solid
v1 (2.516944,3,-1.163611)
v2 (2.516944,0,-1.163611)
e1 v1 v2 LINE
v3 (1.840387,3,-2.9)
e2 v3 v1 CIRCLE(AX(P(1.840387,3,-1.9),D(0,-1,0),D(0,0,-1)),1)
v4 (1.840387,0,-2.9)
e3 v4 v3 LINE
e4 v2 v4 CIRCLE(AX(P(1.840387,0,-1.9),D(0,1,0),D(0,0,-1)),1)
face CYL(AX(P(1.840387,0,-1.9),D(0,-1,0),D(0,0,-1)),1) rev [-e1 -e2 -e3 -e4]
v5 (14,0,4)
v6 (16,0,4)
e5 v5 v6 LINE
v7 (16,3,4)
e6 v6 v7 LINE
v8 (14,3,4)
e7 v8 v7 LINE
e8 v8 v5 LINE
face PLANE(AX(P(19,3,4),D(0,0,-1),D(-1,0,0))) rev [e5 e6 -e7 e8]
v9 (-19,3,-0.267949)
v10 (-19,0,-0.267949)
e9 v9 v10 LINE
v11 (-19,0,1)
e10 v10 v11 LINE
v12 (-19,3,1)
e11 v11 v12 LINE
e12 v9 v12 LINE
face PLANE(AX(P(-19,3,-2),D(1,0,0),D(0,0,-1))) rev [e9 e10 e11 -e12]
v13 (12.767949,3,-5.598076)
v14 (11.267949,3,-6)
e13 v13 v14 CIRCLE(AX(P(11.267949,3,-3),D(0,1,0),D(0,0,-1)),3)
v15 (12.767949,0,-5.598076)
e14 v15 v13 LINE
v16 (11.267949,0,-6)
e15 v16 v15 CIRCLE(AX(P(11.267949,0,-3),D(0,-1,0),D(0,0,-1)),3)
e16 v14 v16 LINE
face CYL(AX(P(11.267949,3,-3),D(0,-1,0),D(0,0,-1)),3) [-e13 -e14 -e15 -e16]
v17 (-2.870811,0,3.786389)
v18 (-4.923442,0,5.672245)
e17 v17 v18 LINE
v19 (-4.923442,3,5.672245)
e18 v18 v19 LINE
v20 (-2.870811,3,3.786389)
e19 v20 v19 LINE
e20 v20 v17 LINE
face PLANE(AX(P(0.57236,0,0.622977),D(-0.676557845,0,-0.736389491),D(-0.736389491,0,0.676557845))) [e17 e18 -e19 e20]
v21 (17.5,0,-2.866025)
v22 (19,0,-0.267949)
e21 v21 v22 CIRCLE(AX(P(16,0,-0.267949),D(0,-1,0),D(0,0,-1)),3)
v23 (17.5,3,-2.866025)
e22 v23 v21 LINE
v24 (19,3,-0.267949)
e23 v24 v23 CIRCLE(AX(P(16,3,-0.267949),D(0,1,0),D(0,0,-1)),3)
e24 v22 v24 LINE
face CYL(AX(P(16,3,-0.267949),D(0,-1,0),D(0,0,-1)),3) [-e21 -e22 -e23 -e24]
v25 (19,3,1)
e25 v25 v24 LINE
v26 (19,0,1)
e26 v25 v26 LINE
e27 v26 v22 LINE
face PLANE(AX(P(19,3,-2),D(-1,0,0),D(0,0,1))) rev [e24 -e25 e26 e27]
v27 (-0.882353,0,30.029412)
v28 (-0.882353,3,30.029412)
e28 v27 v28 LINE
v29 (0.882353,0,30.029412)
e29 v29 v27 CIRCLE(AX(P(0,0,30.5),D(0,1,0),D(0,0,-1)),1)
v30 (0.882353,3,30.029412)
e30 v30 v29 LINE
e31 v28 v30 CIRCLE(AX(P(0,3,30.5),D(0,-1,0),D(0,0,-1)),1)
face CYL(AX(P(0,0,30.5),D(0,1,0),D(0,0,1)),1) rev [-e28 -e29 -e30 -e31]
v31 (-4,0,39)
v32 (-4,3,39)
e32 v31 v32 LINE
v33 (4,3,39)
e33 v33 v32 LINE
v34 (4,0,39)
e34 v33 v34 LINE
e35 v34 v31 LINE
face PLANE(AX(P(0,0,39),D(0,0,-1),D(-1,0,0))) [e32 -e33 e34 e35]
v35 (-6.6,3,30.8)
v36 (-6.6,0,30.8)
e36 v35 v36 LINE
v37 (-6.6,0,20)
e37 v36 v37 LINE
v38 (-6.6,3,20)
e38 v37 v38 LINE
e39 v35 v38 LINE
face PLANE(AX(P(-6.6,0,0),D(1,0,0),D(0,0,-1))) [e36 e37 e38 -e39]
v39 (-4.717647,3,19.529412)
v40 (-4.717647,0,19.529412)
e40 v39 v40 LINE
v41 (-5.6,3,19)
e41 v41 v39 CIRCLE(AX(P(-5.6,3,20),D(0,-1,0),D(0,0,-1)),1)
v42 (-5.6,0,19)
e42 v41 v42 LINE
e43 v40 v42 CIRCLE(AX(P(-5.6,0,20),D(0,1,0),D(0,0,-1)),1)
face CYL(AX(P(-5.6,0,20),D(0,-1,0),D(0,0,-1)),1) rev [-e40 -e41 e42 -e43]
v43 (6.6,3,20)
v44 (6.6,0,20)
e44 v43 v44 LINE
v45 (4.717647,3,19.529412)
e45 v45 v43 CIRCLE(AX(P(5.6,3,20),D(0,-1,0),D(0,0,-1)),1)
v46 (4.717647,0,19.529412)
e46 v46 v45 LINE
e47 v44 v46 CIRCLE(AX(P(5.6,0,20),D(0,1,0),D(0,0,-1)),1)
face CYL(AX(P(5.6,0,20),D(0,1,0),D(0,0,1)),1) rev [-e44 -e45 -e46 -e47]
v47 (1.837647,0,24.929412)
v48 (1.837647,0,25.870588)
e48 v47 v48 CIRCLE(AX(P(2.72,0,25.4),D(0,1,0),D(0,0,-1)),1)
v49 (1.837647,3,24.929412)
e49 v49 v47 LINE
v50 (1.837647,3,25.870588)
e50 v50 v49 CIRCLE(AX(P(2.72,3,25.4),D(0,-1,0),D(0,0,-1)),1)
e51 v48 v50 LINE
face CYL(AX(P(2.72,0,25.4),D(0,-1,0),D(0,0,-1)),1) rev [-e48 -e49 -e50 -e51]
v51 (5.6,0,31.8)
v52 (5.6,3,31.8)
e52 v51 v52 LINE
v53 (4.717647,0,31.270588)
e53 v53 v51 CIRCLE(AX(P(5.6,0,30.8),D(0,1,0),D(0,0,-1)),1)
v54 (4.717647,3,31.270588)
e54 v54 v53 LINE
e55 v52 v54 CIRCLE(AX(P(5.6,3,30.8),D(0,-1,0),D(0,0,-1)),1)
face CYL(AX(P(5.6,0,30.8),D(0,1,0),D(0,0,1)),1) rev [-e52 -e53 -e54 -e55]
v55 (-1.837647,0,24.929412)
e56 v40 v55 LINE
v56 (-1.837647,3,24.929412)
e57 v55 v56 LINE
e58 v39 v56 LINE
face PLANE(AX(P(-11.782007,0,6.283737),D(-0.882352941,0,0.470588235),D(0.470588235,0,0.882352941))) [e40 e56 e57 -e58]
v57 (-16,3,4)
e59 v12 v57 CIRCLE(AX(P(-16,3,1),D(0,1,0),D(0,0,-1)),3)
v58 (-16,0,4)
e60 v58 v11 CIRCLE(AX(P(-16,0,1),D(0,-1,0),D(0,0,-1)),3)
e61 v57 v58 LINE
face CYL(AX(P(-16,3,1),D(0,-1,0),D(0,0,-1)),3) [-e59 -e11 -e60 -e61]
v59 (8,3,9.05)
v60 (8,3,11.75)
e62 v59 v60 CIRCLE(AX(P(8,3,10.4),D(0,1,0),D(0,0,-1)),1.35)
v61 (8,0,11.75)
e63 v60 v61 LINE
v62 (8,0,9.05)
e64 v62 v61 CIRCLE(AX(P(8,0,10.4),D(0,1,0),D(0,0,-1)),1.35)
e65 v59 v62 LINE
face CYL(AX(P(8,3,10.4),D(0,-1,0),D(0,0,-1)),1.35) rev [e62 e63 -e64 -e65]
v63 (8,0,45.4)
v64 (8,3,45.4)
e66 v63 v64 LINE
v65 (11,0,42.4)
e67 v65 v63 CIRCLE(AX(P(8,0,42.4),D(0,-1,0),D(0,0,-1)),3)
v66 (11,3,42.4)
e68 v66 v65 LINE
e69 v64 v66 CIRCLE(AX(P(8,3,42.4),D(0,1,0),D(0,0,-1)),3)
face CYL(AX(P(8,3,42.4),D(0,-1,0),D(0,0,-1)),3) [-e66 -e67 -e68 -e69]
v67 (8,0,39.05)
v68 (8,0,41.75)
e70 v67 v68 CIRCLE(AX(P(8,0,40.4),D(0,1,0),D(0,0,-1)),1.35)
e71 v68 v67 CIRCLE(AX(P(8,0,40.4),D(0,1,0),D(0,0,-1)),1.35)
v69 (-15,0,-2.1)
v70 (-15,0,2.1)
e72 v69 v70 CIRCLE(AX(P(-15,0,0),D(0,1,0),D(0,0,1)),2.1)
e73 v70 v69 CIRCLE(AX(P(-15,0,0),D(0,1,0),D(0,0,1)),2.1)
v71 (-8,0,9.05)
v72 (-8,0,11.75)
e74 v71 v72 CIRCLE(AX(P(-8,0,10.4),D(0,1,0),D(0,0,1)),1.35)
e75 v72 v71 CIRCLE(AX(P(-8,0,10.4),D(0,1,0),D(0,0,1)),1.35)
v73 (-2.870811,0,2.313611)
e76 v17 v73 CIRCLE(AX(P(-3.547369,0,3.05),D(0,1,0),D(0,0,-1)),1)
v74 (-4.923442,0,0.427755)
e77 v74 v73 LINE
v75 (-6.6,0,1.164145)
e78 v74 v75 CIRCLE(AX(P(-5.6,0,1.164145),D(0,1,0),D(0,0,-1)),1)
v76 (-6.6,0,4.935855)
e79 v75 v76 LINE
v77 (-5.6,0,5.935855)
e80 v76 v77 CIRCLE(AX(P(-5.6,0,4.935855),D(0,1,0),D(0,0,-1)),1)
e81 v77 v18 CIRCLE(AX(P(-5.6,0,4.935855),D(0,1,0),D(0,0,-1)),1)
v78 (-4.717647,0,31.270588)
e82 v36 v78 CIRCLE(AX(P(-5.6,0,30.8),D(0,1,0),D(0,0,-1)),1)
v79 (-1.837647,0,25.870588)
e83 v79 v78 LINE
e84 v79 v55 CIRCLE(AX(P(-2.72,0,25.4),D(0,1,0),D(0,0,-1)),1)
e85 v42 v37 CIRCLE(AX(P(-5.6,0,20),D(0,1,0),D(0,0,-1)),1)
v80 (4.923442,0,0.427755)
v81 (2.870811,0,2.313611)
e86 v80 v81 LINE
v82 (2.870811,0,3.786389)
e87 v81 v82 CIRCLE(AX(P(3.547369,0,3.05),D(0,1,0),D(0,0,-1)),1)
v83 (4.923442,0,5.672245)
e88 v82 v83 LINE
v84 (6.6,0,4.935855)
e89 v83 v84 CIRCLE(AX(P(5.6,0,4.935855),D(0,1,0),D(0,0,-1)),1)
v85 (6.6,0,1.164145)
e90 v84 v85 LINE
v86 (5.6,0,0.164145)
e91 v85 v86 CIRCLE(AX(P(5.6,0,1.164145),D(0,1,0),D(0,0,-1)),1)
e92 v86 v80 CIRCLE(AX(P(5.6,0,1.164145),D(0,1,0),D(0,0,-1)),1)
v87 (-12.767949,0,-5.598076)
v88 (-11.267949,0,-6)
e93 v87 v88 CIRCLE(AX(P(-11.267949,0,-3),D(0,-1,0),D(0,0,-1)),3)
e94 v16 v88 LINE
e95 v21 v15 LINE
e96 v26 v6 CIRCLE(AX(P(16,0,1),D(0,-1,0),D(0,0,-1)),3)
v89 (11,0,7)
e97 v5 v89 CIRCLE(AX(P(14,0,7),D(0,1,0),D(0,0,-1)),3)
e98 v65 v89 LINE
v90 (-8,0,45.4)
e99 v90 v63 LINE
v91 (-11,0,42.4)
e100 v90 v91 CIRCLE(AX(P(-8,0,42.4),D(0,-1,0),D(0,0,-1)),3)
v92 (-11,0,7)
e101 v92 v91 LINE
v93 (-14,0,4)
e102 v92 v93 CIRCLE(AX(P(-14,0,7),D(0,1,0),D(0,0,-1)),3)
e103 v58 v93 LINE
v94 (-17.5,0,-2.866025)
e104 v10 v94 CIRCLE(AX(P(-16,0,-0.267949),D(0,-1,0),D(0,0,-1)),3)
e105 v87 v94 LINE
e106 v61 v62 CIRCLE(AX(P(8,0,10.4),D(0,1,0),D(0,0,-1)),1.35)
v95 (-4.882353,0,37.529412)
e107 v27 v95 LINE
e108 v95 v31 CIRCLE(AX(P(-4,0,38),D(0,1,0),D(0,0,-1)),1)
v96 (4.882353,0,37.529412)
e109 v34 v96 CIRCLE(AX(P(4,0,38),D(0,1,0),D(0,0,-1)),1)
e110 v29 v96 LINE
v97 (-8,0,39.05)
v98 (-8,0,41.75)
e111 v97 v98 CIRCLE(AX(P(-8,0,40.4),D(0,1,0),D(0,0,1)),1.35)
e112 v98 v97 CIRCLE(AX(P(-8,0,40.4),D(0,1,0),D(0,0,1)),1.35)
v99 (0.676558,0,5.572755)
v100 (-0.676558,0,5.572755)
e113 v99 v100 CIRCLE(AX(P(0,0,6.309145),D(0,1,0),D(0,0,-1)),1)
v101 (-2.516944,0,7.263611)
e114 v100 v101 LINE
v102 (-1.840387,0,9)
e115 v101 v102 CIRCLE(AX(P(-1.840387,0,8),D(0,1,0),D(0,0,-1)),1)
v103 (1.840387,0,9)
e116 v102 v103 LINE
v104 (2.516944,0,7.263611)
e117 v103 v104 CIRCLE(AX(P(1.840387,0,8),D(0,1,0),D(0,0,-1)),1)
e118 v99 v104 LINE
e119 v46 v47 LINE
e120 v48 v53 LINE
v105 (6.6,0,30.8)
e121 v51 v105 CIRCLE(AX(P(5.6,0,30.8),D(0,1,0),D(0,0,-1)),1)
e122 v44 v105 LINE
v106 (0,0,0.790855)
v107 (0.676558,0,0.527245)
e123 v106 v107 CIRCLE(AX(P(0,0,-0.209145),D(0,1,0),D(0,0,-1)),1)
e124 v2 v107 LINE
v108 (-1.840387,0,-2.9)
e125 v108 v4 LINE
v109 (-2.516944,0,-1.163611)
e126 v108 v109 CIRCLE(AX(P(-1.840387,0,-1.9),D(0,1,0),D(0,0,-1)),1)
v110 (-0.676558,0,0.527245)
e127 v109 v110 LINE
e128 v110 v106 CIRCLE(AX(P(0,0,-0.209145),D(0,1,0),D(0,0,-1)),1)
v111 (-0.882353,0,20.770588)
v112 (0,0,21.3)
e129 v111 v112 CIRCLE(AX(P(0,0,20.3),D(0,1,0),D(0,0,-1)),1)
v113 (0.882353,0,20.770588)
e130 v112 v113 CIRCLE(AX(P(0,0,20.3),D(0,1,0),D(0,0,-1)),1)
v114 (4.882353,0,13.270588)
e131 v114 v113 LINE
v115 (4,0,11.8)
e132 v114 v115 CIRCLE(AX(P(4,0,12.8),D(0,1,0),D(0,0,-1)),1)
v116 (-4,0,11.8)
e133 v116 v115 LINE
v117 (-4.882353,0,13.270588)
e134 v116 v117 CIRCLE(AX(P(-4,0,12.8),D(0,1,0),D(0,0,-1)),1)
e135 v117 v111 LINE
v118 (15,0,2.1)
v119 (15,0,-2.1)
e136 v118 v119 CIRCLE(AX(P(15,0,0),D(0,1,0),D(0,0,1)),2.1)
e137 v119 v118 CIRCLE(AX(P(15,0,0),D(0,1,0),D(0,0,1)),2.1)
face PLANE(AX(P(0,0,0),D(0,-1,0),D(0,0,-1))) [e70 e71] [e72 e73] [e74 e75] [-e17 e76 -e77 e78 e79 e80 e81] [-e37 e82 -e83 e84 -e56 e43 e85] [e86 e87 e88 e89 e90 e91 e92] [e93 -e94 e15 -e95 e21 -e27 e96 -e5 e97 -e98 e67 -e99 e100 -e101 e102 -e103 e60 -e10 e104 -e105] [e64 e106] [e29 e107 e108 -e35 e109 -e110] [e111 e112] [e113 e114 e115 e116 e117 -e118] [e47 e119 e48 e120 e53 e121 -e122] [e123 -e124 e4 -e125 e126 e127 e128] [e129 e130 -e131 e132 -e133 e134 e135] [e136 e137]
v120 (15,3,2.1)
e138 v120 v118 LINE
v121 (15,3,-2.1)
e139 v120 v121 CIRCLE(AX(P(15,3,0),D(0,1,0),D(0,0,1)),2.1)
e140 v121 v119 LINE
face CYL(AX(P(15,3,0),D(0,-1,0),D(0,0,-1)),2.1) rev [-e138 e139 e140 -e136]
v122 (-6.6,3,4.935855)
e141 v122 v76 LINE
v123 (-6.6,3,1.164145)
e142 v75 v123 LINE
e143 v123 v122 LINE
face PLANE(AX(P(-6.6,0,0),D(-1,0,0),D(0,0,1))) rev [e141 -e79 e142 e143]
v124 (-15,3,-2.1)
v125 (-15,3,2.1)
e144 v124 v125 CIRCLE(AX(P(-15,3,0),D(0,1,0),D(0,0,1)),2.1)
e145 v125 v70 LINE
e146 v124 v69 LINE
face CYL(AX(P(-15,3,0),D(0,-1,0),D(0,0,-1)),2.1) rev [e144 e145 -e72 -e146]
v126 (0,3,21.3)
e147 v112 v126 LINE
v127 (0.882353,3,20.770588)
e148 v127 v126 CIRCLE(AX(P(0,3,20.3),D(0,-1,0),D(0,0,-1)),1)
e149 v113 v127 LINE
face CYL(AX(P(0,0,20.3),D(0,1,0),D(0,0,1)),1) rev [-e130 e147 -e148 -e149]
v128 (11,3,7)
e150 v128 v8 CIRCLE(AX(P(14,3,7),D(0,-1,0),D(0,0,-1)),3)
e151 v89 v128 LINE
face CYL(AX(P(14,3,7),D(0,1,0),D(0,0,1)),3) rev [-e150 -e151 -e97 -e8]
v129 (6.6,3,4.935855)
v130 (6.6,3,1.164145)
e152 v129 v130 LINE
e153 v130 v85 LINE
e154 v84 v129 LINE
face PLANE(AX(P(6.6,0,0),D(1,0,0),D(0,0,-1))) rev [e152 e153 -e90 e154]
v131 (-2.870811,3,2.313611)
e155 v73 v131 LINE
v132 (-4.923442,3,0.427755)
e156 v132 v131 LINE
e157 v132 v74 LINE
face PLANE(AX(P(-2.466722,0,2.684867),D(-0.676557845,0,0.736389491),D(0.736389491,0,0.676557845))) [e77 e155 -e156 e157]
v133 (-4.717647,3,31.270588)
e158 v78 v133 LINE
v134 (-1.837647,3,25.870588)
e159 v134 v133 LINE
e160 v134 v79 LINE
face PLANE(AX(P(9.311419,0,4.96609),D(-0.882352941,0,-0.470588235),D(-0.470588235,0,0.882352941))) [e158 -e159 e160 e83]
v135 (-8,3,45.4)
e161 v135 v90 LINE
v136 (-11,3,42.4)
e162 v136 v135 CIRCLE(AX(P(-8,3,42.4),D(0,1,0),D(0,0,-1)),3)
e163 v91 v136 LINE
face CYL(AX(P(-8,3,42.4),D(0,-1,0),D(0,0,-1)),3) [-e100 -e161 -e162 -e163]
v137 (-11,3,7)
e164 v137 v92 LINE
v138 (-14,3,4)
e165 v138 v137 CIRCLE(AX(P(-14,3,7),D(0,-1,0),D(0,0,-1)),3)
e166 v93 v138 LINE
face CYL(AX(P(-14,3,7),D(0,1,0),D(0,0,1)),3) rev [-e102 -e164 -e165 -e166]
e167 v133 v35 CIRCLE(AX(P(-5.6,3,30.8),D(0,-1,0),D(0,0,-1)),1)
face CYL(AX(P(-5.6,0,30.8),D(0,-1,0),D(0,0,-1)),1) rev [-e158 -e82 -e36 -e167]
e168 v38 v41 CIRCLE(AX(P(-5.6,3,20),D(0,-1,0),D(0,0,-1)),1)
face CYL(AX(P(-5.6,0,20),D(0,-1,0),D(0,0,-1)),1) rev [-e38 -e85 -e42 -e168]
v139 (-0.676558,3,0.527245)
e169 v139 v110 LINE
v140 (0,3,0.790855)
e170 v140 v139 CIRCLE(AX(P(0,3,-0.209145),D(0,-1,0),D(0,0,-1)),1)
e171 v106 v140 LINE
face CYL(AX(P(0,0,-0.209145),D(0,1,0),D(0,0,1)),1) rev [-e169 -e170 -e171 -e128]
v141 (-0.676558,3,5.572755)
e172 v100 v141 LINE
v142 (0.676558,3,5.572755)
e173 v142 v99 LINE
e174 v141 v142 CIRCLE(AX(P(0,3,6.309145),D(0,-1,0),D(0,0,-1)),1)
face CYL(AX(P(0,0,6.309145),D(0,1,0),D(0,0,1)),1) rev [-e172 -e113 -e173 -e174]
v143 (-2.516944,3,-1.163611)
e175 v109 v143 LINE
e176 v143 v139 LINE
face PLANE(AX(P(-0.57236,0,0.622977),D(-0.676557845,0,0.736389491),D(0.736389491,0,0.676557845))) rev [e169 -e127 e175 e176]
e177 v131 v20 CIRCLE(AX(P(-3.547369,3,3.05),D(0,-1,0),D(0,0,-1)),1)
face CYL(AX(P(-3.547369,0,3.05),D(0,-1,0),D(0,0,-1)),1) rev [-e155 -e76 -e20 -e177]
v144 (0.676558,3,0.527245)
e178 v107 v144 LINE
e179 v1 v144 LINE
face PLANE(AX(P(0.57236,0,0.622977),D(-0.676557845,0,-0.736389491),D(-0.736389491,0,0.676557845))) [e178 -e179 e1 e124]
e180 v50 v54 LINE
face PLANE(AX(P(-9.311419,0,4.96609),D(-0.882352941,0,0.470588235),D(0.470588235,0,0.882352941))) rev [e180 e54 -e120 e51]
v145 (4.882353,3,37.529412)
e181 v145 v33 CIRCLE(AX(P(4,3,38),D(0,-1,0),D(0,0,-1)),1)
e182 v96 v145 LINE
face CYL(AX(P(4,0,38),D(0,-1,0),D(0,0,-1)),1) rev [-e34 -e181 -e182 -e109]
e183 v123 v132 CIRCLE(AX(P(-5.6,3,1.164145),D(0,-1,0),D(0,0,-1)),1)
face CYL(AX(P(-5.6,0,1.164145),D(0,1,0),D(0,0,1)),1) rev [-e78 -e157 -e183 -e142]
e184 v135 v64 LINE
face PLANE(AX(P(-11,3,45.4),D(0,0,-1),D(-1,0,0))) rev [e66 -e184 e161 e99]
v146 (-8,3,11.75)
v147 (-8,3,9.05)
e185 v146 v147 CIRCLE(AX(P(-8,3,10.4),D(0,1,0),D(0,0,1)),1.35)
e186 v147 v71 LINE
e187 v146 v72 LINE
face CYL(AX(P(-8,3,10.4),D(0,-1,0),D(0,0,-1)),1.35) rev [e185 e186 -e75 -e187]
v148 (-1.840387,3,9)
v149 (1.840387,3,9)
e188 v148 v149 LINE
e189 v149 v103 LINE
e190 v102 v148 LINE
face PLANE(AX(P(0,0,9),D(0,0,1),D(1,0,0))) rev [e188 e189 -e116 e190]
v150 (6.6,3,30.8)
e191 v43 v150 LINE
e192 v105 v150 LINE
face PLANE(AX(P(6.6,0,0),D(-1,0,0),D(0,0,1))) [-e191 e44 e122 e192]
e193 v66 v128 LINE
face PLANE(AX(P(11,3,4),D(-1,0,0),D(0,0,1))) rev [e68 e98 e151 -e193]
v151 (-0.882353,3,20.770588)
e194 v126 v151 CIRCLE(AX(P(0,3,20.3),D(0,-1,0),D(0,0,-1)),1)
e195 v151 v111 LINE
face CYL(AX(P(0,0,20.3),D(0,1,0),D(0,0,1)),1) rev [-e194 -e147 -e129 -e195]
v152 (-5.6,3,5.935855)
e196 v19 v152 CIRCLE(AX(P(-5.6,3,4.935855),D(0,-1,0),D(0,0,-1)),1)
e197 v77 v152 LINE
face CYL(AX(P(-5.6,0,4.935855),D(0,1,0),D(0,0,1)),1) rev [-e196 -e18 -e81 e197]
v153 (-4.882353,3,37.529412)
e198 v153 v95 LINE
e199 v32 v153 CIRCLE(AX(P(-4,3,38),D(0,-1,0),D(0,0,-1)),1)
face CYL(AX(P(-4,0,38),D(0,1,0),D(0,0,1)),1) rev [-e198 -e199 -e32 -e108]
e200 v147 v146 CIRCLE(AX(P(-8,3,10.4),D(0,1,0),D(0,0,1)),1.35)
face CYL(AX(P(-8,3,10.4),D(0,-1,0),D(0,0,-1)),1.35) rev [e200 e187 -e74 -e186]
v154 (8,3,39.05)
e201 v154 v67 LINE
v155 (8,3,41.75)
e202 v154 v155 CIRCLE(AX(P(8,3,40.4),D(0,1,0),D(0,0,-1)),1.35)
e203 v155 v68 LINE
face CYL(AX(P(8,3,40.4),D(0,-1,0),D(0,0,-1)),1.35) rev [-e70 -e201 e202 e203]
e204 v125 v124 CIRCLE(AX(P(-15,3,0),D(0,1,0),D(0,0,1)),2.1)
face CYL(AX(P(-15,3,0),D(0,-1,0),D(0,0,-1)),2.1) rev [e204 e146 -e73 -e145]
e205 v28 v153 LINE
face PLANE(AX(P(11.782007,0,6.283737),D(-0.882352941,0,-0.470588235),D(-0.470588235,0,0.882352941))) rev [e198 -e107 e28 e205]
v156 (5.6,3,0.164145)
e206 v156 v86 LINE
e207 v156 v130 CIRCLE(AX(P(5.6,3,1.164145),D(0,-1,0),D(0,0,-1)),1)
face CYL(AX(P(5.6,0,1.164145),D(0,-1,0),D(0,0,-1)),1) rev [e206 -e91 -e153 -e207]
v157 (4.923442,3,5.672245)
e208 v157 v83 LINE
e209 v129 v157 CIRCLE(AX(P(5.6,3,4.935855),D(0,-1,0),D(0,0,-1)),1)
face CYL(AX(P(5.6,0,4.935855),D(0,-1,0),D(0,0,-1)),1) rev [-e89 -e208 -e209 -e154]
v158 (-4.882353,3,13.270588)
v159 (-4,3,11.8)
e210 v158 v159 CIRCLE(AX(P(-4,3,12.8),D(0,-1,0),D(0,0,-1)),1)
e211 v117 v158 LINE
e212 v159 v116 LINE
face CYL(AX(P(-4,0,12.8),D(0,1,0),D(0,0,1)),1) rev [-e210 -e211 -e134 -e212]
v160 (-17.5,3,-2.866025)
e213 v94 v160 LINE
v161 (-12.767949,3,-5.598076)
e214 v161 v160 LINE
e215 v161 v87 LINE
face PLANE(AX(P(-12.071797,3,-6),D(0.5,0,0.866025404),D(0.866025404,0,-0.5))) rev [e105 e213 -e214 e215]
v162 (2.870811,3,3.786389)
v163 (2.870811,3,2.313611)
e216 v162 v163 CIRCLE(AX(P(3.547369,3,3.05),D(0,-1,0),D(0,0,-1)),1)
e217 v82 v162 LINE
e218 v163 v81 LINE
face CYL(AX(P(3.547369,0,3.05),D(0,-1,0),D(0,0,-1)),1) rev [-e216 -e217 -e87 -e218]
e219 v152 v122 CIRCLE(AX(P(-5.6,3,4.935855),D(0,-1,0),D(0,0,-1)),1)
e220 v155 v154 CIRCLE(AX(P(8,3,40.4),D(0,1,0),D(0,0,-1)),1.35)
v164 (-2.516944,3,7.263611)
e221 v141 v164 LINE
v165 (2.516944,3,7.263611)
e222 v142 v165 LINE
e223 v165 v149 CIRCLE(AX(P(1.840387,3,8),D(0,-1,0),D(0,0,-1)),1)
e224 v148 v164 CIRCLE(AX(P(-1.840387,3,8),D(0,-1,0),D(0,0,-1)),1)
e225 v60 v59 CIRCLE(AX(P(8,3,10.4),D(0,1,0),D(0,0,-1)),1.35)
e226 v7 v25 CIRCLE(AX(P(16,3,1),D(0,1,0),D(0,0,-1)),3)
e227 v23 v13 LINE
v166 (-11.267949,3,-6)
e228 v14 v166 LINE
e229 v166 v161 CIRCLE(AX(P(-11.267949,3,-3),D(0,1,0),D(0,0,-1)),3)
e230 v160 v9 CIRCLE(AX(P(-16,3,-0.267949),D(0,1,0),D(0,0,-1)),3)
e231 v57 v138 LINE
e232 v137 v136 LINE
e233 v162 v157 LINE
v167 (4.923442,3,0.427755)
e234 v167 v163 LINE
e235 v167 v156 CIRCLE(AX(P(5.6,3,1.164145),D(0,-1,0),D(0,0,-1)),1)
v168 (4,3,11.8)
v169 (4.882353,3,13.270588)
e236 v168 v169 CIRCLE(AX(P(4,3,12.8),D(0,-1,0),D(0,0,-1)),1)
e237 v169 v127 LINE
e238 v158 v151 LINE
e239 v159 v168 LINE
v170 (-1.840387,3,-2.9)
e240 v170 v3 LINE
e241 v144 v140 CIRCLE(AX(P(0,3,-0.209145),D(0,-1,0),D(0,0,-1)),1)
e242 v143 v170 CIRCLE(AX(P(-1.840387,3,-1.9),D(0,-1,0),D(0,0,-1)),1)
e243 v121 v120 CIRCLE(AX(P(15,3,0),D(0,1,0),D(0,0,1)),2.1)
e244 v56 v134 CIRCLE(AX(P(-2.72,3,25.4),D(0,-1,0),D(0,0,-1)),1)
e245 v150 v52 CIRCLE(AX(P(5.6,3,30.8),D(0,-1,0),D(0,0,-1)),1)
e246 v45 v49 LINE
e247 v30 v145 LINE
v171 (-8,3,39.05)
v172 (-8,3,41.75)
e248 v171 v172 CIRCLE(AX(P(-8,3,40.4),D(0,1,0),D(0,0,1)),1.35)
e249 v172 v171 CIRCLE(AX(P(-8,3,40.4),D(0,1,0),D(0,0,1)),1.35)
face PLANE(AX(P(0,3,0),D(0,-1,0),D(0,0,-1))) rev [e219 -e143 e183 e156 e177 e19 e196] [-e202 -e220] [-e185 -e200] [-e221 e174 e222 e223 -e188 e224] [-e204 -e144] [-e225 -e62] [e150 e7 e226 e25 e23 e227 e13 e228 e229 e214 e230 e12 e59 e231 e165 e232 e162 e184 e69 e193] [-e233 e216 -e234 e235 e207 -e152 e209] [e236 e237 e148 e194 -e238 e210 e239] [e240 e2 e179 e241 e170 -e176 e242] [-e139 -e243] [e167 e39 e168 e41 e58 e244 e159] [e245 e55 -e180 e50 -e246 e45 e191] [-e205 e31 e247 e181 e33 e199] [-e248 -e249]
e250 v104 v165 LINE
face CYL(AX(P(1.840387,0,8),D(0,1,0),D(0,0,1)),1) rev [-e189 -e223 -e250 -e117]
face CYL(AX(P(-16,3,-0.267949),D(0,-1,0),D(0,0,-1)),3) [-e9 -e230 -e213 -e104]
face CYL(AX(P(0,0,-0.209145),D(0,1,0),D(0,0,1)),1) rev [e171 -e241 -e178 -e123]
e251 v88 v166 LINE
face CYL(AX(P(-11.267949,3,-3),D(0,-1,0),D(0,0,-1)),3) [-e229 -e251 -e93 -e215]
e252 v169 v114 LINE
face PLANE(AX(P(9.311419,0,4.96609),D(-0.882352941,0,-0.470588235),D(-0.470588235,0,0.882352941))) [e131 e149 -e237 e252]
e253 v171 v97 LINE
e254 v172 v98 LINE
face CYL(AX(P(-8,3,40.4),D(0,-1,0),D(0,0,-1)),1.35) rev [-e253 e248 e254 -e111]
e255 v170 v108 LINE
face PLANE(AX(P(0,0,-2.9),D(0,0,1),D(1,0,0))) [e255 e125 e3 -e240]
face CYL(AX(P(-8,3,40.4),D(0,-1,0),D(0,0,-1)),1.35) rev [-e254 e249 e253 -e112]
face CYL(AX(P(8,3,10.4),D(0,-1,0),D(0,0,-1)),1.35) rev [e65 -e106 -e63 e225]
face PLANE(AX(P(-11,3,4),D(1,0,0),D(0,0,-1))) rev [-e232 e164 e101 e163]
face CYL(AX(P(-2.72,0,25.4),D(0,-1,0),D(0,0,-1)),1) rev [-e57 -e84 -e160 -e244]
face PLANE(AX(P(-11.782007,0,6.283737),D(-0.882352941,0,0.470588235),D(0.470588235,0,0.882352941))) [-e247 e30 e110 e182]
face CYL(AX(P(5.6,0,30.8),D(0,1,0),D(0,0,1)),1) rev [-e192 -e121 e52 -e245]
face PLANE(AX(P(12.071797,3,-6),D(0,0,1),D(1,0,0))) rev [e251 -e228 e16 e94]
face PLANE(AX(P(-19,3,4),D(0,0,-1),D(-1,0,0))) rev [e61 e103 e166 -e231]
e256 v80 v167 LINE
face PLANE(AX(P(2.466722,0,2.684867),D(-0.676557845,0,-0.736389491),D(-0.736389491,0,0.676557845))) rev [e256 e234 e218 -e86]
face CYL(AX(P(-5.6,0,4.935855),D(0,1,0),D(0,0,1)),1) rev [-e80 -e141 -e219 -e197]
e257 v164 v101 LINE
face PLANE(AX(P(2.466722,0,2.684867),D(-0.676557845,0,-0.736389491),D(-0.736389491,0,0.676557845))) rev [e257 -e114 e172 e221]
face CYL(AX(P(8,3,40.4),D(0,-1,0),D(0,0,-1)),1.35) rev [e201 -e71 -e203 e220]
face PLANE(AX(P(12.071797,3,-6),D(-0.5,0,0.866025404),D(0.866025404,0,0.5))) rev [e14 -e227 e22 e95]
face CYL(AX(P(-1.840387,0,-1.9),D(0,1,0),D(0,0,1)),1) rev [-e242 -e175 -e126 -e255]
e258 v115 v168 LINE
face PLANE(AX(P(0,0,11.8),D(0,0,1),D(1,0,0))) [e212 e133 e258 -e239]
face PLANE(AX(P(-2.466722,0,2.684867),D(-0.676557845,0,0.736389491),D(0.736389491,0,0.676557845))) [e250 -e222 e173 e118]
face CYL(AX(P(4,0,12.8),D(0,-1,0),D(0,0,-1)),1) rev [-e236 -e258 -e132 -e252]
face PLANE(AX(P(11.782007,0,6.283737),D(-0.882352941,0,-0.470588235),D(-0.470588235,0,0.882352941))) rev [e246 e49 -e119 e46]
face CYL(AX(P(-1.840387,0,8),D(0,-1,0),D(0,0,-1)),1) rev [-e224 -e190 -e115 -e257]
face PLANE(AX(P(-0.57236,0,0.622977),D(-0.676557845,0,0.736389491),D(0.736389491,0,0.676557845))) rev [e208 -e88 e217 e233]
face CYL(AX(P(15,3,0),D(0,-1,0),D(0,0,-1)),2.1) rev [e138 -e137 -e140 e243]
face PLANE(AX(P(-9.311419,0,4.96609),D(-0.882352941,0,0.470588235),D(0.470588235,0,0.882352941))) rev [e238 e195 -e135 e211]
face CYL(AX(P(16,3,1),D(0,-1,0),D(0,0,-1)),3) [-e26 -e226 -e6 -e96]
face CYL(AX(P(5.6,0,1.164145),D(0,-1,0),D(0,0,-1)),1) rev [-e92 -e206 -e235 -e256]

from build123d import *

# Parameters (mm, degrees)
SKETCH_1_R          = 2.1
SKETCH_1_R_2        = 1.35
EXTRUDE_1_DEPTH     = 3
CUT_EXTRUDE_1_DEPTH = 50.306794664
FILLET_R3_R         = 3
FILLET_R1_R         = 1


with BuildPart() as part:
    # 草图1 → 凸台-拉伸1 (new body)
    with BuildSketch(Plane(origin=(0, 0, 0), x_dir=(1, 0, 0), z_dir=(0, 1, 0))):
        Polygon((-12.07179677, 6), (-19, 2), (-19, -4), (-11, -4), (-11, -45.4), (11, -45.4), (11, -4), (19, -4), (19, 2), (12.07179677, 6), align=None)
        with Locations(Location((-15, 0, 0), (0, 0, 270))):
            Circle(SKETCH_1_R, mode=Mode.SUBTRACT)
        with Locations(Location((15, 0, 0), (0, 0, 270))):
            Circle(SKETCH_1_R, mode=Mode.SUBTRACT)
        with Locations(Location((-8, -10.4, 0), (0, 0, 270))):
            Circle(SKETCH_1_R_2, mode=Mode.SUBTRACT)
        with Locations(Location((-8, -40.4, 0), (0, 0, 270))):
            Circle(SKETCH_1_R_2, mode=Mode.SUBTRACT)
        with Locations(Location((8, -10.4, 0), (0, 0, 90))):
            Circle(SKETCH_1_R_2, mode=Mode.SUBTRACT)
        with Locations(Location((8, -40.4, 0), (0, 0, 90))):
            Circle(SKETCH_1_R_2, mode=Mode.SUBTRACT)
    extrude(amount=EXTRUDE_1_DEPTH)

    # 草图2 → 切除-拉伸1 (cut, through all)
    with BuildSketch(Plane(origin=(0, 3, 0), x_dir=(1, 0, 0), z_dir=(0, 1, 0))):
        Polygon((-6.6, 1.112582185), (-6.6, -7.212582185), (-2.069298303, -3.05), align=None)
        Polygon((-4.406892174, 2.9), (0, -1.148832185), (4.406892174, 2.9), align=None)
        Polygon((6.6, 1.112582185), (2.069298303, -3.05), (6.6, -7.212582185), align=None)
        Polygon((0, -4.951167815), (-4.406892174, -9), (4.406892174, -9), align=None)
        Polygon((5.666666667, -11.8), (-5.666666667, -11.8), (0, -22.425), align=None)
        Polygon((-1.586666667, -25.4), (-6.6, -16), (-6.6, -34.8), align=None)
        Polygon((5.666666667, -39), (0, -28.375), (-5.666666667, -39), align=None)
        Polygon((6.6, -16), (1.586666667, -25.4), (6.6, -34.8), align=None)
    extrude(amount=-CUT_EXTRUDE_1_DEPTH, mode=Mode.SUBTRACT)

    # R3 外缘圆角
    fillet_r3_edges = [part.edges().sort_by_distance(p)[0] for p in [
        (19, 1.5, 4),
        (11, 1.5, 4),
        (11, 1.5, 45.4),
        (-11, 1.5, 45.4),
        (-11, 1.5, 4),
        (-19, 1.5, 4),
        (-19, 1.5, -2),
        (-12.07179677, 1.5, -6),
        (12.07179677, 1.5, -6),
        (19, 1.5, -2),
    ]]
    fillet(fillet_r3_edges, radius=FILLET_R3_R)

    # R1 镂空圆角
    fillet_r1_edges = [part.edges().sort_by_distance(p)[0] for p in [
        (6.6, 1.5, 16),
        (6.6, 1.5, 34.8),
        (1.586666667, 1.5, 25.4),
        (-6.6, 1.5, 34.8),
        (-6.6, 1.5, 16),
        (-1.586666667, 1.5, 25.4),
        (5.666666667, 1.5, 39),
        (-5.666666667, 1.5, 39),
        (0, 1.5, 28.375),
        (-2.069298303, 1.5, 3.05),
        (-6.6, 1.5, 7.212582185),
        (-6.6, 1.5, -1.112582185),
        (-5.666666667, 1.5, 11.8),
        (5.666666667, 1.5, 11.8),
        (0, 1.5, 22.425),
        (0, 1.5, 4.951167815),
        (4.406892174, 1.5, 9),
        (-4.406892174, 1.5, 9),
        (4.406892174, 1.5, -2.9),
        (0, 1.5, 1.148832185),
        (-4.406892174, 1.5, -2.9),
        (6.6, 1.5, -1.112582185),
        (6.6, 1.5, 7.212582185),
        (2.069298303, 1.5, 3.05),
    ]]
    fillet(fillet_r1_edges, radius=FILLET_R1_R)


solid = part.part
